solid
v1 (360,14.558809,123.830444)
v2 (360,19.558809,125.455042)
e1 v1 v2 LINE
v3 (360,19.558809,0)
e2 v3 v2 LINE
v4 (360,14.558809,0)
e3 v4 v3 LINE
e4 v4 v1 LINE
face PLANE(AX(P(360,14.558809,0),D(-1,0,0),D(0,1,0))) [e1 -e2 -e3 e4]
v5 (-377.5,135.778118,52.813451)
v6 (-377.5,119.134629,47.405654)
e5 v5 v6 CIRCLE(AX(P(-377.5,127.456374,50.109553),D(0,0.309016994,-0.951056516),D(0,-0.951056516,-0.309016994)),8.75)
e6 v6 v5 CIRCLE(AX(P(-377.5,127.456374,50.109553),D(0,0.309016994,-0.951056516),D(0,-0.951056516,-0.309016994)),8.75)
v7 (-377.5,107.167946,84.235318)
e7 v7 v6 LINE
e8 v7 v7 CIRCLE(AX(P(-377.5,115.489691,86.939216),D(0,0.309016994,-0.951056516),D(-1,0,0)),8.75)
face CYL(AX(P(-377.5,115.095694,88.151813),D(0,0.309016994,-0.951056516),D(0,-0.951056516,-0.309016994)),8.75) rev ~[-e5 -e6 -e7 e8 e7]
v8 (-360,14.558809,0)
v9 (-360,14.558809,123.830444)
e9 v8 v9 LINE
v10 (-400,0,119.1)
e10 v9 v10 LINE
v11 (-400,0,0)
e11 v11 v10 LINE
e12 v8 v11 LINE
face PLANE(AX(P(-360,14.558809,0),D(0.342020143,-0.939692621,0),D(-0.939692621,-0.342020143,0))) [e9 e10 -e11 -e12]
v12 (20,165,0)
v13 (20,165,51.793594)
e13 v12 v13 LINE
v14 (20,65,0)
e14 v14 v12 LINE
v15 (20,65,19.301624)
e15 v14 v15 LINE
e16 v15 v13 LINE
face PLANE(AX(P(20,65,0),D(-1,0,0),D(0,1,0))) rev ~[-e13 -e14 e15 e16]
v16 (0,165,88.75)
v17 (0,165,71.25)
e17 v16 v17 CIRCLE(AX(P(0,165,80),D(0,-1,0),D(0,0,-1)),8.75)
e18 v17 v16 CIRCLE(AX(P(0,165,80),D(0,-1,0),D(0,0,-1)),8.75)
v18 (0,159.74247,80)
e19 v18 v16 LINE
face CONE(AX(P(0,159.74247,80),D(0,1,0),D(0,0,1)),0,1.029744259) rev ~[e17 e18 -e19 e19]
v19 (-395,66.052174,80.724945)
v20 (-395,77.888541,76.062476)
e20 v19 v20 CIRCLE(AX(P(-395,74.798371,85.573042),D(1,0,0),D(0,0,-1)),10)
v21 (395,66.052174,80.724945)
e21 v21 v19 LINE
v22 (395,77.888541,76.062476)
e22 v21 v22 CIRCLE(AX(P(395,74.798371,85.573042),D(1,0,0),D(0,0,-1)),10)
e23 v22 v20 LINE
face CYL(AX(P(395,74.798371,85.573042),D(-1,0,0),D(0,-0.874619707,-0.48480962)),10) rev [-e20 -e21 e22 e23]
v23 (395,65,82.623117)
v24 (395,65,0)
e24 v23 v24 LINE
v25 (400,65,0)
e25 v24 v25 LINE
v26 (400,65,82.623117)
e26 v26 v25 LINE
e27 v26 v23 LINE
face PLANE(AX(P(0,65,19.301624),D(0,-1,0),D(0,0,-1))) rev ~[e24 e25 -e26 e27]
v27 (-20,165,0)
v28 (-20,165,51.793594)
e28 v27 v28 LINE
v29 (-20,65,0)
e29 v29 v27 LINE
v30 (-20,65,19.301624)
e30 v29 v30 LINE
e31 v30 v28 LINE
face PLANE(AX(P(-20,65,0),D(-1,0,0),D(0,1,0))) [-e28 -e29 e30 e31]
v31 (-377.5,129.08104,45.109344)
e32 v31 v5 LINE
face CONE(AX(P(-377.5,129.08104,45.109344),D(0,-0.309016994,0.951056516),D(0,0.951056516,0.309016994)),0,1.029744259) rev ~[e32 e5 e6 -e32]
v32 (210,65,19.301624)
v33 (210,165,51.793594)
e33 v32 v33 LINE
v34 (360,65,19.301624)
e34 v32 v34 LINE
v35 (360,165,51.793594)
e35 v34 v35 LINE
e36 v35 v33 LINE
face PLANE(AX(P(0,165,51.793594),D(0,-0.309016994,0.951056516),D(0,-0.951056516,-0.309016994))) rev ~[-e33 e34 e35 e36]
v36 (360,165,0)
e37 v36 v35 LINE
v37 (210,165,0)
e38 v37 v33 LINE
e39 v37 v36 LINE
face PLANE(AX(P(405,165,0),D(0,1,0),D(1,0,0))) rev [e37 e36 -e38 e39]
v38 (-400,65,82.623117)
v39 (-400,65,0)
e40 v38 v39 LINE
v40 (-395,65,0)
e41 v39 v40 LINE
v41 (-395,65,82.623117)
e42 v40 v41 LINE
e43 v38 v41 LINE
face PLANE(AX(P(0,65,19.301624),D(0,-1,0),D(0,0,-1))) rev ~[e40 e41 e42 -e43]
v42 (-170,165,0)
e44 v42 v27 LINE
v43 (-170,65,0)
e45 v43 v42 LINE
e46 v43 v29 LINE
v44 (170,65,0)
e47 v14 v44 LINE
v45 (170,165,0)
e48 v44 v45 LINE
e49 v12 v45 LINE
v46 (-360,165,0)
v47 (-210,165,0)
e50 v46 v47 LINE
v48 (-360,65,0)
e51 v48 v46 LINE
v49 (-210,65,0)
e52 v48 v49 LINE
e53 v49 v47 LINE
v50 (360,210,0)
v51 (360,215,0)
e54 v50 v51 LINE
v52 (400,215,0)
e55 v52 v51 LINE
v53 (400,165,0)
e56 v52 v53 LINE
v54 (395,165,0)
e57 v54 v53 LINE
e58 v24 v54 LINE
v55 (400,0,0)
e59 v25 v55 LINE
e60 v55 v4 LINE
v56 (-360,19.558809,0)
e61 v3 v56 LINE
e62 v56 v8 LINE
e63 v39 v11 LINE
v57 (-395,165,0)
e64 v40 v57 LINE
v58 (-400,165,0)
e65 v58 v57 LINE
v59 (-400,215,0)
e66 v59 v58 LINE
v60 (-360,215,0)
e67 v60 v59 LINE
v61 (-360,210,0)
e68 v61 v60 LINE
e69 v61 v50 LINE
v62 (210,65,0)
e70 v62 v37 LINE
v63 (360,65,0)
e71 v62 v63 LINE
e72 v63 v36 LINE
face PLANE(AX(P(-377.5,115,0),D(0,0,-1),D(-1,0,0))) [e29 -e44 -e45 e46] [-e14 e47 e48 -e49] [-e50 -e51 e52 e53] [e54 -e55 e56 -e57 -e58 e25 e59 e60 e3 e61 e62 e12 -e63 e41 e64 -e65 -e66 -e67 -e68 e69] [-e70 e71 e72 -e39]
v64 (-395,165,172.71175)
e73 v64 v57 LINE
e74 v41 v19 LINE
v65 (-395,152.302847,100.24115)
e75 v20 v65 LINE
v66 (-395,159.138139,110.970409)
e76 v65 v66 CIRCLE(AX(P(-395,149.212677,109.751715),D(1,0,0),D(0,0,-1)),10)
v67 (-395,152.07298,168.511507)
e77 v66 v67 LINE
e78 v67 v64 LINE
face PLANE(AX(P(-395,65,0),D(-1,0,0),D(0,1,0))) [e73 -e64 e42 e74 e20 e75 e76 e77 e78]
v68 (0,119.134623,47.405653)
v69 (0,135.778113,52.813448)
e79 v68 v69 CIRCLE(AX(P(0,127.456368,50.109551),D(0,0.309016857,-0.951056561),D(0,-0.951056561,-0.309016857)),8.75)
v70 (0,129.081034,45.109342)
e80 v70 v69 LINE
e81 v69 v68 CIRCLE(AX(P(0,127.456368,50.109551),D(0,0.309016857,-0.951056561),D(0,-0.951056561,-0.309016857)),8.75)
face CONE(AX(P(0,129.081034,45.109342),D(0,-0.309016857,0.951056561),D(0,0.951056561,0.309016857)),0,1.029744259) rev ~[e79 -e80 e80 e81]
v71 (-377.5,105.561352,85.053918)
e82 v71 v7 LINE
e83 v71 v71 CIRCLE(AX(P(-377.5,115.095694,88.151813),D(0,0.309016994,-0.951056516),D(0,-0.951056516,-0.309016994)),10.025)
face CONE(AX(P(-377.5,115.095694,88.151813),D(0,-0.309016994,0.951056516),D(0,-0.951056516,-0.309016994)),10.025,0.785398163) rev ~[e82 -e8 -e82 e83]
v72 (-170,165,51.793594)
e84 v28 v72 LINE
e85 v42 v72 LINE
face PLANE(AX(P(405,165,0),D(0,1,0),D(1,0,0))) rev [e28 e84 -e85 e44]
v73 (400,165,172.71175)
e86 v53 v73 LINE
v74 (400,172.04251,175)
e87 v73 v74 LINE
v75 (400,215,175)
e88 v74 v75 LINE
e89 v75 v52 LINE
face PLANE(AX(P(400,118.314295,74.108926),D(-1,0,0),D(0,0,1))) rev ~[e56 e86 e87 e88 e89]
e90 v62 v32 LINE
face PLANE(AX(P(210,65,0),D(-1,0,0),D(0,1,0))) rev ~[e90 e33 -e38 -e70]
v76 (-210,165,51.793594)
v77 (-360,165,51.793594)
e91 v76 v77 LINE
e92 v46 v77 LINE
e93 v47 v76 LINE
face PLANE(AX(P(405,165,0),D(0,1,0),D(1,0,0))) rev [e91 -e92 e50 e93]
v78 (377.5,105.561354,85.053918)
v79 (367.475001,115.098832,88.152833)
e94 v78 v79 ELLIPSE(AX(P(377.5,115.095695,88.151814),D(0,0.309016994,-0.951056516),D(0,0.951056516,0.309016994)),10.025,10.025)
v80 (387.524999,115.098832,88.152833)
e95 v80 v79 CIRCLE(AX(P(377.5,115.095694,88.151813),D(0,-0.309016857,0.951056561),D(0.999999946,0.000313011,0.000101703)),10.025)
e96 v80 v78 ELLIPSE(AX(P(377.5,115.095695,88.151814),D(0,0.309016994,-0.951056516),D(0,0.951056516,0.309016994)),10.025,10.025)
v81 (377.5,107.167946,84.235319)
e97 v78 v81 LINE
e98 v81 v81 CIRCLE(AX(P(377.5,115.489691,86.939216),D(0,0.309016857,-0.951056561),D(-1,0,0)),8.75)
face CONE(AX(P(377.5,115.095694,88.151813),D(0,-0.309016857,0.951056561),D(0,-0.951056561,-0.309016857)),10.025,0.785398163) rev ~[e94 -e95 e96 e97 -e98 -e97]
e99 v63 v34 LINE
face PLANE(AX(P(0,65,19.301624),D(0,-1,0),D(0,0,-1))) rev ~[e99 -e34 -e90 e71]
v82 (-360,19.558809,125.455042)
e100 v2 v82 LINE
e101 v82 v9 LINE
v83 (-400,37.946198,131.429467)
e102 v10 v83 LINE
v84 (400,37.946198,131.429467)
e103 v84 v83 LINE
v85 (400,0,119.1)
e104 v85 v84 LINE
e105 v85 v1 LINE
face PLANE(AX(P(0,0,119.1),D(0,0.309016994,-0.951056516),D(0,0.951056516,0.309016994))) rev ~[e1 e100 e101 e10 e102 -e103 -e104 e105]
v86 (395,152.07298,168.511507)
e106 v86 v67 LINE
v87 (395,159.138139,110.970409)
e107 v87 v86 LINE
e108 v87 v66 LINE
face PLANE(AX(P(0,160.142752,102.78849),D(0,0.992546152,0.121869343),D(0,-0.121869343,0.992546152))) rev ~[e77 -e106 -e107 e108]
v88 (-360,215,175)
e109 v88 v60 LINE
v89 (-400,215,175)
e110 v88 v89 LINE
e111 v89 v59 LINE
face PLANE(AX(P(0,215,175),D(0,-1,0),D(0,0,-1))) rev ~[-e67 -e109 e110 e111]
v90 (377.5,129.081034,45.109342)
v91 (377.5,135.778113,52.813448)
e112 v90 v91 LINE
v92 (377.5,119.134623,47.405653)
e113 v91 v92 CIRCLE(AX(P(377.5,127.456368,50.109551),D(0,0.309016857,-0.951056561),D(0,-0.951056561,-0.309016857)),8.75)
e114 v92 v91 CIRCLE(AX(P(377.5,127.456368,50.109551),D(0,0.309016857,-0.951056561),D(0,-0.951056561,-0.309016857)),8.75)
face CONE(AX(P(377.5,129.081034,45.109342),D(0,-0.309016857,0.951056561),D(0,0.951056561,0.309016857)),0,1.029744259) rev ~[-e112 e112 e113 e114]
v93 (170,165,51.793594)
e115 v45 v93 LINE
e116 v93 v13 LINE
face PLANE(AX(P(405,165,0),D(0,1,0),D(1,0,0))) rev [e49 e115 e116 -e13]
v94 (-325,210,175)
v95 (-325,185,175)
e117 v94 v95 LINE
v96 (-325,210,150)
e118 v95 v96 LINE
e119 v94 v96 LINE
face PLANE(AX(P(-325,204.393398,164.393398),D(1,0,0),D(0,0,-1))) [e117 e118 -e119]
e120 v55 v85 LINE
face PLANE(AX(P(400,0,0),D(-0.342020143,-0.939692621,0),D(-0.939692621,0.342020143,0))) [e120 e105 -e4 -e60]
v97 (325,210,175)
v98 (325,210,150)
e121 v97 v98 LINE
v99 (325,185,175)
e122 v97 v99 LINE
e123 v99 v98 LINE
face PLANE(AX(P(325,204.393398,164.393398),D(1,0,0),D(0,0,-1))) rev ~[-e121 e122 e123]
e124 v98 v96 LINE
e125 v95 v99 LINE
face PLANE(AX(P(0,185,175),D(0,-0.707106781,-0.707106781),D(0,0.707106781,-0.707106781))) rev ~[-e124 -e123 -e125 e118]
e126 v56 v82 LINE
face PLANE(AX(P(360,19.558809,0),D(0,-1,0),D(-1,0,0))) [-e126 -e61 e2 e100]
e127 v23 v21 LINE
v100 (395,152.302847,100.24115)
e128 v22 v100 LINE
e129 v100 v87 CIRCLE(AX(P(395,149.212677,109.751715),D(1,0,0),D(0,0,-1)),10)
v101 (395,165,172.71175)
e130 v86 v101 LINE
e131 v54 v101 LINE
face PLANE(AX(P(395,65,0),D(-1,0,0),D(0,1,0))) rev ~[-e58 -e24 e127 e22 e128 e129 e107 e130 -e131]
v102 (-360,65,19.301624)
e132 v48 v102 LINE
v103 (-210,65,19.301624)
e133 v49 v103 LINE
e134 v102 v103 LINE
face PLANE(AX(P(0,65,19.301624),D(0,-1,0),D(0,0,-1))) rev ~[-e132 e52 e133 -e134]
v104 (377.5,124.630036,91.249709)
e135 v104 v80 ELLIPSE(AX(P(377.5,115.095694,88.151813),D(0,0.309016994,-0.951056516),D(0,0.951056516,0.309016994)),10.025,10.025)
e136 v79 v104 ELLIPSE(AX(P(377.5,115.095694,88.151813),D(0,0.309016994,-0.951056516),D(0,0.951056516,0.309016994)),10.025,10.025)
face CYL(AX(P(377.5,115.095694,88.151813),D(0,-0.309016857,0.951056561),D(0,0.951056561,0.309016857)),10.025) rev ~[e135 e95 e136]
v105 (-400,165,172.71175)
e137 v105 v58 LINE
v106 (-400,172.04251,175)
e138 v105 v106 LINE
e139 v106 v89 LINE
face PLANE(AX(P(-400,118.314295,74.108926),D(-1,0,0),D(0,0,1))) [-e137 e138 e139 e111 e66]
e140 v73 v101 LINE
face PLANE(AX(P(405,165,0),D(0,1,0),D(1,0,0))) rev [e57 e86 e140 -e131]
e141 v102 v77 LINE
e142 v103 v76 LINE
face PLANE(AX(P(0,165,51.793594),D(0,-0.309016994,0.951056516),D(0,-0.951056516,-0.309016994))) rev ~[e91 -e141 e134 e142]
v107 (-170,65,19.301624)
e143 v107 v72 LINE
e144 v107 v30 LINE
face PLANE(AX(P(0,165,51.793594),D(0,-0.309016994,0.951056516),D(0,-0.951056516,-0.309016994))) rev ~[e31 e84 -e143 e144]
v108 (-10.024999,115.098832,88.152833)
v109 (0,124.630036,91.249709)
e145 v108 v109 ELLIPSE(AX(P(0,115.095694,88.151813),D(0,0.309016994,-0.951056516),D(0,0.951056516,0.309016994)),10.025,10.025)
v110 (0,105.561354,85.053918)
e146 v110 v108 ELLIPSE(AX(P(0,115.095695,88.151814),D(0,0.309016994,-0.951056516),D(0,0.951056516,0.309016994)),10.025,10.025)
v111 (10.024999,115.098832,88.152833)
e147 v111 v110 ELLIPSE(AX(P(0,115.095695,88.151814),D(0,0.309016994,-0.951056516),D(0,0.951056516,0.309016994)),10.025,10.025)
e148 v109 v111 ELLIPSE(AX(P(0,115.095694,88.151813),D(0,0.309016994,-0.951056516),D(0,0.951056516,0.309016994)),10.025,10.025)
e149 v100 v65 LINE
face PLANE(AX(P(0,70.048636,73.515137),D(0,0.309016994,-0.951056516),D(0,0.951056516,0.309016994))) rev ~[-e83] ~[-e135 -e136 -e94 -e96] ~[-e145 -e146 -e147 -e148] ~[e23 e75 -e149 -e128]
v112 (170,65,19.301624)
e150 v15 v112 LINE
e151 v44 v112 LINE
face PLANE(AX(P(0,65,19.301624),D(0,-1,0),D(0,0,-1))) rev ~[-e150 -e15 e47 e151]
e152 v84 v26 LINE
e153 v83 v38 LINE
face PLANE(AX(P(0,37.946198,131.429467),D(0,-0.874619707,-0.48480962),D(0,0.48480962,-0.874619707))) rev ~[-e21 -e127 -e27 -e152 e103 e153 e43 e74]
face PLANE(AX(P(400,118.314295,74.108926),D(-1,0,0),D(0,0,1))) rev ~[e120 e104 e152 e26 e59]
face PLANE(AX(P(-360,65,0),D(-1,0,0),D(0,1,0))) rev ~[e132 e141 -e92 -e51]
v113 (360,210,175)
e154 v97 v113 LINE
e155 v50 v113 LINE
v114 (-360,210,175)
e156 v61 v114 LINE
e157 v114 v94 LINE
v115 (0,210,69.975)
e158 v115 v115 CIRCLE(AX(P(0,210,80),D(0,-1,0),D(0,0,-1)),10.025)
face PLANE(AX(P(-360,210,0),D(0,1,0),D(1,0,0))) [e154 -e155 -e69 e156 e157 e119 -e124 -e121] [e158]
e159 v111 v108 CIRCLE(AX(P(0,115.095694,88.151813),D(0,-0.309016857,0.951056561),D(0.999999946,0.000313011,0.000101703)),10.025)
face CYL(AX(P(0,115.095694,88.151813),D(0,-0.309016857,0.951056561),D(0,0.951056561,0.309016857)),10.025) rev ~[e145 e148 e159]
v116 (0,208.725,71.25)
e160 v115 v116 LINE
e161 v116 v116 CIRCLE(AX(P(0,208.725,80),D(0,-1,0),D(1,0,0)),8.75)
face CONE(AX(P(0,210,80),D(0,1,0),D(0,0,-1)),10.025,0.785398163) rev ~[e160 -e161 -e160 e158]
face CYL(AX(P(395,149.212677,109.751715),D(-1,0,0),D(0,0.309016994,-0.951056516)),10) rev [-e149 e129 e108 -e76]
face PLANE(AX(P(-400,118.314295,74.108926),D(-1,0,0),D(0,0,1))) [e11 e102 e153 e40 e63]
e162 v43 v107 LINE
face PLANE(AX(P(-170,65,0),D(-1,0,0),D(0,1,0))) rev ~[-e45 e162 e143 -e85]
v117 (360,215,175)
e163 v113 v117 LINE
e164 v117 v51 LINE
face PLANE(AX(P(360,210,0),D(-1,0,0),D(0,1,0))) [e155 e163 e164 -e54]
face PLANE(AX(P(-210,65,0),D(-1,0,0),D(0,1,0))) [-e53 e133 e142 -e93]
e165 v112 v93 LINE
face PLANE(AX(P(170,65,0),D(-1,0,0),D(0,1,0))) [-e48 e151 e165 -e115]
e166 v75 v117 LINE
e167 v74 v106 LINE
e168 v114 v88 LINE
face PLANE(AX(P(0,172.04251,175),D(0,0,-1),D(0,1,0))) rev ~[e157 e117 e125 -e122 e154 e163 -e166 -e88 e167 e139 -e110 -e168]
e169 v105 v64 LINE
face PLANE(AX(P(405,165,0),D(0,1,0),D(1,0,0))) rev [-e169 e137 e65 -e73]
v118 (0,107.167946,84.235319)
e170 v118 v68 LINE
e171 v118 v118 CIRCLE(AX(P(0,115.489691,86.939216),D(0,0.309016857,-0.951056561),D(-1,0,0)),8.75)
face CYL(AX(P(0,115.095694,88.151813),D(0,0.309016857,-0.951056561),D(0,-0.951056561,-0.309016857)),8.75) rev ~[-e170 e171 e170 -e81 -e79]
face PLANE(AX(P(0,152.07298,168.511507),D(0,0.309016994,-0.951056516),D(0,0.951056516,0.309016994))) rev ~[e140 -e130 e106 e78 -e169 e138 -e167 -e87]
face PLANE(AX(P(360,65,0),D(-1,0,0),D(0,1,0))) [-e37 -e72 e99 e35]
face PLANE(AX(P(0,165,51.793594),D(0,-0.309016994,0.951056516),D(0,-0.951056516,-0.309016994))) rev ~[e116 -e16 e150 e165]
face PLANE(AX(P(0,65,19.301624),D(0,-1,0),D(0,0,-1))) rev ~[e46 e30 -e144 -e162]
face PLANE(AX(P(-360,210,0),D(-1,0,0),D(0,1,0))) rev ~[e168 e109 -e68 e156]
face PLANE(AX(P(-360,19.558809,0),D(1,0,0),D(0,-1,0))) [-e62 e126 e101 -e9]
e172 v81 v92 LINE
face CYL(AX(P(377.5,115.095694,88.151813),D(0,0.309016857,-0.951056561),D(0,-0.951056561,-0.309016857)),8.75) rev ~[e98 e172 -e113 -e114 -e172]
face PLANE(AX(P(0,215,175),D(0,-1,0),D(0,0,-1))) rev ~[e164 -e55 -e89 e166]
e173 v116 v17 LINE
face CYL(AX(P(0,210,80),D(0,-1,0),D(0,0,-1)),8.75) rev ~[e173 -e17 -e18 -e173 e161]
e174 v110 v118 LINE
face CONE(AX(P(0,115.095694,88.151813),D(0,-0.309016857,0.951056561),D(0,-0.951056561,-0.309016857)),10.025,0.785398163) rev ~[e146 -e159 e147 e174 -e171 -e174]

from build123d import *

# Parameters (mm, degrees)
BOSS_EXTRUDE1_DEPTH                    = 400
SKETCH3_W                              = 720
SKETCH3_H                              = 10
CUT_EXTRUDE1_DEPTH                     = 487.672374396
CUT_EXTRUDE2_DEPTH                     = 325
CUT_EXTRUDE3_DEPTH                     = 650
SKETCH7_W                              = 10
SKETCH7_H                              = 100
CUT_EXTRUDE4_DEPTH                     = 650
BOSS_EXTRUDE2_REACH                    = 488.672
SKETCH8_W                              = 40
SKETCH8_H                              = 100
SKETCH8_W_2                            = 35
M20_TAPPED_HOLE1_D                     = 17.5
M20_TAPPED_HOLE1_DEPTH                 = 45
M20_TAPPED_HOLE1_CSINK_D               = 20.05
M20_TAPPED_HOLE1_CSINK_ANGLE           = 90
M20_TAPPED_HOLE1_TIP                   = 5.257530416
M20_TAPPED_HOLE2_D                     = 17.5
M20_TAPPED_HOLE2_DEPTH                 = 40
M20_TAPPED_HOLE2_CSINK_D               = 20.05
M20_TAPPED_HOLE2_CSINK_ANGLE           = 90
M20_TAPPED_HOLE2_TIP                   = 5.257530416
M20_TAPPED_HOLE2_ON_FACE_2_D           = 17.5
M20_TAPPED_HOLE2_ON_FACE_2_DEPTH       = 40
M20_TAPPED_HOLE2_ON_FACE_2_CSINK_D     = 20.05
M20_TAPPED_HOLE2_ON_FACE_2_CSINK_ANGLE = 90
M20_TAPPED_HOLE2_ON_FACE_2_TIP         = 5.257530416
FILLET1_R                              = 10


with BuildPart() as part:
    # Sketch1 → Boss-Extrude1 (new, symmetric)
    with BuildSketch(Plane(origin=(0, 0, 0), x_dir=(0, 0, -1), z_dir=(1, 0, 0))):
        Polygon((0, 0), (-119.1, 0), (-131.429467258, 37.946198403), (-73.515136927, 70.048635914), (-102.788489796, 160.142752116), (-168.511506583, 152.072980358), (-175, 172.042509728), (-175, 215), (0, 215), (0, 165), (-51.793594091, 165), (-19.301624468, 65), (0, 65), align=None)
    extrude(amount=BOSS_EXTRUDE1_DEPTH, both=True)

    # Sketch3 → Cut-Extrude1 (cut, through all)
    with BuildSketch(Plane.XY):
        with Locations((0, 215)):
            Rectangle(SKETCH3_W, SKETCH3_H)
    extrude(amount=CUT_EXTRUDE1_DEPTH, mode=Mode.SUBTRACT)

    # Sketch4 → Cut-Extrude2 (cut, symmetric)
    with BuildSketch(Plane(origin=(0, 0, 0), x_dir=(0, 0, -1), z_dir=(1, 0, 0))):
        Polygon((-175, 215), (-175, 185), (-145, 215), align=None)
    extrude(amount=CUT_EXTRUDE2_DEPTH, both=True, mode=Mode.SUBTRACT)

    # Sketch6 → Cut-Extrude3 (cut)
    with BuildSketch(Plane(origin=(0, 0, 0), x_dir=(-1, 0, 0), z_dir=(0, 0, -1))):
        Polygon((-400, 0), (-360, 14.558809371), (-360, 19.558809371), (360, 19.558809371), (360, 14.558809371), (400, 0), align=None)
    extrude(amount=-CUT_EXTRUDE3_DEPTH, mode=Mode.SUBTRACT)

    # Sketch7 → Cut-Extrude4 (cut)
    with BuildSketch(Plane.XY):
        with Locations((-400, 115)):
            Rectangle(SKETCH7_W, SKETCH7_H)
    cut_extrude4 = extrude(amount=CUT_EXTRUDE4_DEPTH, mode=Mode.SUBTRACT)

    # Mirror1: Cut-Extrude4 across plane
    add(cut_extrude4.mirror(Plane(origin=(0, 0, 0), x_dir=(0, 0, 1), z_dir=(1, 0, 0))), mode=Mode.SUBTRACT)

    # Boss-Extrude2: up to this plane
    boss_extrude2_end = Plane(origin=(400, 165, 51.793594091), z_dir=(0, -0.309016994374942, 0.9510565162951553))
    # Sketch8 → Boss-Extrude2 (add, up to the surface)
    with BuildSketch(Plane(origin=(0, 0, 0), x_dir=(-1, 0, 0), z_dir=(0, 0, -1)), mode=Mode.PRIVATE) as boss_extrude2_sk1:
        with Locations((0, 115)):
            Rectangle(SKETCH8_W, SKETCH8_H)
    boss_extrude2_tool1 = split(extrude(boss_extrude2_sk1.sketch, amount=-BOSS_EXTRUDE2_REACH, mode=Mode.PRIVATE), bisect_by=boss_extrude2_end, keep=Keep.BOTH, mode=Mode.PRIVATE)
    add(boss_extrude2_tool1.solids().sort_by_distance((0, 115, 0))[0])
    # Sketch8 → Boss-Extrude2 (add, up to the surface)
    with BuildSketch(Plane(origin=(0, 0, 0), x_dir=(-1, 0, 0), z_dir=(0, 0, -1)), mode=Mode.PRIVATE) as boss_extrude2_sk2:
        with Locations((-190, 115)):
            Rectangle(SKETCH8_W, SKETCH8_H)
    boss_extrude2_tool2 = split(extrude(boss_extrude2_sk2.sketch, amount=-BOSS_EXTRUDE2_REACH, mode=Mode.PRIVATE), bisect_by=boss_extrude2_end, keep=Keep.BOTH, mode=Mode.PRIVATE)
    add(boss_extrude2_tool2.solids().sort_by_distance((190, 115, 0))[0])
    # Sketch8 → Boss-Extrude2 (add, up to the surface)
    with BuildSketch(Plane(origin=(0, 0, 0), x_dir=(-1, 0, 0), z_dir=(0, 0, -1)), mode=Mode.PRIVATE) as boss_extrude2_sk3:
        with Locations((190, 115)):
            Rectangle(SKETCH8_W, SKETCH8_H)
    boss_extrude2_tool3 = split(extrude(boss_extrude2_sk3.sketch, amount=-BOSS_EXTRUDE2_REACH, mode=Mode.PRIVATE), bisect_by=boss_extrude2_end, keep=Keep.BOTH, mode=Mode.PRIVATE)
    add(boss_extrude2_tool3.solids().sort_by_distance((-190, 115, 0))[0])
    # Sketch8 → Boss-Extrude2 (add, up to the surface)
    with BuildSketch(Plane(origin=(0, 0, 0), x_dir=(-1, 0, 0), z_dir=(0, 0, -1)), mode=Mode.PRIVATE) as boss_extrude2_sk4:
        with Locations((-377.5, 115)):
            Rectangle(SKETCH8_W_2, SKETCH8_H)
    boss_extrude2_tool4 = split(extrude(boss_extrude2_sk4.sketch, amount=-BOSS_EXTRUDE2_REACH, mode=Mode.PRIVATE), bisect_by=boss_extrude2_end, keep=Keep.BOTH, mode=Mode.PRIVATE)
    add(boss_extrude2_tool4.solids().sort_by_distance((377.5, 115, 0))[0])
    # Sketch8 → Boss-Extrude2 (add, up to the surface)
    with BuildSketch(Plane(origin=(0, 0, 0), x_dir=(-1, 0, 0), z_dir=(0, 0, -1)), mode=Mode.PRIVATE) as boss_extrude2_sk5:
        with Locations((377.5, 115)):
            Rectangle(SKETCH8_W_2, SKETCH8_H)
    boss_extrude2_tool5 = split(extrude(boss_extrude2_sk5.sketch, amount=-BOSS_EXTRUDE2_REACH, mode=Mode.PRIVATE), bisect_by=boss_extrude2_end, keep=Keep.BOTH, mode=Mode.PRIVATE)
    add(boss_extrude2_tool5.solids().sort_by_distance((-377.5, 115, 0))[0])

    # M20 Tapped Hole1
    with Locations(Plane(origin=(0, 210, 80), x_dir=(0, 0, 1), z_dir=(0, 1, 0))):
        with Locations((0, 0)):
            CounterSinkHole(M20_TAPPED_HOLE1_D / 2, M20_TAPPED_HOLE1_CSINK_D / 2, depth=M20_TAPPED_HOLE1_DEPTH, counter_sink_angle=M20_TAPPED_HOLE1_CSINK_ANGLE)
            with Locations((0, 0, -(M20_TAPPED_HOLE1_DEPTH + M20_TAPPED_HOLE1_TIP / 2))):  # 118° drill point
                Cone(0, M20_TAPPED_HOLE1_D / 2, M20_TAPPED_HOLE1_TIP, mode=Mode.SUBTRACT)

    # M20 Tapped Hole2
    with Locations(Plane(origin=(-377.5, 115.095694015, 88.151813362), x_dir=(0, 0.951056516295, 0.309016994375), z_dir=(0, -0.309016994375, 0.951056516295))):
        with Locations((0, 0)):
            CounterSinkHole(M20_TAPPED_HOLE2_D / 2, M20_TAPPED_HOLE2_CSINK_D / 2, depth=M20_TAPPED_HOLE2_DEPTH, counter_sink_angle=M20_TAPPED_HOLE2_CSINK_ANGLE)
            with Locations((0, 0, -(M20_TAPPED_HOLE2_DEPTH + M20_TAPPED_HOLE2_TIP / 2))):  # 118° drill point
                Cone(0, M20_TAPPED_HOLE2_D / 2, M20_TAPPED_HOLE2_TIP, mode=Mode.SUBTRACT)

    # M20 Tapped Hole2 on face 2
    with Locations(Plane(origin=(0, 115.095694015, 88.151813362), x_dir=(0, 0.951056560832, 0.309016857306), z_dir=(0, -0.309016857306, 0.951056560832))):
        with Locations((0, 0), (0, -377.5)):
            CounterSinkHole(M20_TAPPED_HOLE2_ON_FACE_2_D / 2, M20_TAPPED_HOLE2_ON_FACE_2_CSINK_D / 2, depth=M20_TAPPED_HOLE2_ON_FACE_2_DEPTH, counter_sink_angle=M20_TAPPED_HOLE2_ON_FACE_2_CSINK_ANGLE)
            with Locations((0, 0, -(M20_TAPPED_HOLE2_ON_FACE_2_DEPTH + M20_TAPPED_HOLE2_ON_FACE_2_TIP / 2))):  # 118° drill point
                Cone(0, M20_TAPPED_HOLE2_ON_FACE_2_D / 2, M20_TAPPED_HOLE2_ON_FACE_2_TIP, mode=Mode.SUBTRACT)

    # Fillet1
    fillet1_edges = [part.edges().sort_by_distance(p)[0] for p in [
        (0, 70.048635914, 73.515136927),
        (0, 160.142752116, 102.788489796),
    ]]
    fillet(fillet1_edges, radius=FILLET1_R)


solid = part.part
